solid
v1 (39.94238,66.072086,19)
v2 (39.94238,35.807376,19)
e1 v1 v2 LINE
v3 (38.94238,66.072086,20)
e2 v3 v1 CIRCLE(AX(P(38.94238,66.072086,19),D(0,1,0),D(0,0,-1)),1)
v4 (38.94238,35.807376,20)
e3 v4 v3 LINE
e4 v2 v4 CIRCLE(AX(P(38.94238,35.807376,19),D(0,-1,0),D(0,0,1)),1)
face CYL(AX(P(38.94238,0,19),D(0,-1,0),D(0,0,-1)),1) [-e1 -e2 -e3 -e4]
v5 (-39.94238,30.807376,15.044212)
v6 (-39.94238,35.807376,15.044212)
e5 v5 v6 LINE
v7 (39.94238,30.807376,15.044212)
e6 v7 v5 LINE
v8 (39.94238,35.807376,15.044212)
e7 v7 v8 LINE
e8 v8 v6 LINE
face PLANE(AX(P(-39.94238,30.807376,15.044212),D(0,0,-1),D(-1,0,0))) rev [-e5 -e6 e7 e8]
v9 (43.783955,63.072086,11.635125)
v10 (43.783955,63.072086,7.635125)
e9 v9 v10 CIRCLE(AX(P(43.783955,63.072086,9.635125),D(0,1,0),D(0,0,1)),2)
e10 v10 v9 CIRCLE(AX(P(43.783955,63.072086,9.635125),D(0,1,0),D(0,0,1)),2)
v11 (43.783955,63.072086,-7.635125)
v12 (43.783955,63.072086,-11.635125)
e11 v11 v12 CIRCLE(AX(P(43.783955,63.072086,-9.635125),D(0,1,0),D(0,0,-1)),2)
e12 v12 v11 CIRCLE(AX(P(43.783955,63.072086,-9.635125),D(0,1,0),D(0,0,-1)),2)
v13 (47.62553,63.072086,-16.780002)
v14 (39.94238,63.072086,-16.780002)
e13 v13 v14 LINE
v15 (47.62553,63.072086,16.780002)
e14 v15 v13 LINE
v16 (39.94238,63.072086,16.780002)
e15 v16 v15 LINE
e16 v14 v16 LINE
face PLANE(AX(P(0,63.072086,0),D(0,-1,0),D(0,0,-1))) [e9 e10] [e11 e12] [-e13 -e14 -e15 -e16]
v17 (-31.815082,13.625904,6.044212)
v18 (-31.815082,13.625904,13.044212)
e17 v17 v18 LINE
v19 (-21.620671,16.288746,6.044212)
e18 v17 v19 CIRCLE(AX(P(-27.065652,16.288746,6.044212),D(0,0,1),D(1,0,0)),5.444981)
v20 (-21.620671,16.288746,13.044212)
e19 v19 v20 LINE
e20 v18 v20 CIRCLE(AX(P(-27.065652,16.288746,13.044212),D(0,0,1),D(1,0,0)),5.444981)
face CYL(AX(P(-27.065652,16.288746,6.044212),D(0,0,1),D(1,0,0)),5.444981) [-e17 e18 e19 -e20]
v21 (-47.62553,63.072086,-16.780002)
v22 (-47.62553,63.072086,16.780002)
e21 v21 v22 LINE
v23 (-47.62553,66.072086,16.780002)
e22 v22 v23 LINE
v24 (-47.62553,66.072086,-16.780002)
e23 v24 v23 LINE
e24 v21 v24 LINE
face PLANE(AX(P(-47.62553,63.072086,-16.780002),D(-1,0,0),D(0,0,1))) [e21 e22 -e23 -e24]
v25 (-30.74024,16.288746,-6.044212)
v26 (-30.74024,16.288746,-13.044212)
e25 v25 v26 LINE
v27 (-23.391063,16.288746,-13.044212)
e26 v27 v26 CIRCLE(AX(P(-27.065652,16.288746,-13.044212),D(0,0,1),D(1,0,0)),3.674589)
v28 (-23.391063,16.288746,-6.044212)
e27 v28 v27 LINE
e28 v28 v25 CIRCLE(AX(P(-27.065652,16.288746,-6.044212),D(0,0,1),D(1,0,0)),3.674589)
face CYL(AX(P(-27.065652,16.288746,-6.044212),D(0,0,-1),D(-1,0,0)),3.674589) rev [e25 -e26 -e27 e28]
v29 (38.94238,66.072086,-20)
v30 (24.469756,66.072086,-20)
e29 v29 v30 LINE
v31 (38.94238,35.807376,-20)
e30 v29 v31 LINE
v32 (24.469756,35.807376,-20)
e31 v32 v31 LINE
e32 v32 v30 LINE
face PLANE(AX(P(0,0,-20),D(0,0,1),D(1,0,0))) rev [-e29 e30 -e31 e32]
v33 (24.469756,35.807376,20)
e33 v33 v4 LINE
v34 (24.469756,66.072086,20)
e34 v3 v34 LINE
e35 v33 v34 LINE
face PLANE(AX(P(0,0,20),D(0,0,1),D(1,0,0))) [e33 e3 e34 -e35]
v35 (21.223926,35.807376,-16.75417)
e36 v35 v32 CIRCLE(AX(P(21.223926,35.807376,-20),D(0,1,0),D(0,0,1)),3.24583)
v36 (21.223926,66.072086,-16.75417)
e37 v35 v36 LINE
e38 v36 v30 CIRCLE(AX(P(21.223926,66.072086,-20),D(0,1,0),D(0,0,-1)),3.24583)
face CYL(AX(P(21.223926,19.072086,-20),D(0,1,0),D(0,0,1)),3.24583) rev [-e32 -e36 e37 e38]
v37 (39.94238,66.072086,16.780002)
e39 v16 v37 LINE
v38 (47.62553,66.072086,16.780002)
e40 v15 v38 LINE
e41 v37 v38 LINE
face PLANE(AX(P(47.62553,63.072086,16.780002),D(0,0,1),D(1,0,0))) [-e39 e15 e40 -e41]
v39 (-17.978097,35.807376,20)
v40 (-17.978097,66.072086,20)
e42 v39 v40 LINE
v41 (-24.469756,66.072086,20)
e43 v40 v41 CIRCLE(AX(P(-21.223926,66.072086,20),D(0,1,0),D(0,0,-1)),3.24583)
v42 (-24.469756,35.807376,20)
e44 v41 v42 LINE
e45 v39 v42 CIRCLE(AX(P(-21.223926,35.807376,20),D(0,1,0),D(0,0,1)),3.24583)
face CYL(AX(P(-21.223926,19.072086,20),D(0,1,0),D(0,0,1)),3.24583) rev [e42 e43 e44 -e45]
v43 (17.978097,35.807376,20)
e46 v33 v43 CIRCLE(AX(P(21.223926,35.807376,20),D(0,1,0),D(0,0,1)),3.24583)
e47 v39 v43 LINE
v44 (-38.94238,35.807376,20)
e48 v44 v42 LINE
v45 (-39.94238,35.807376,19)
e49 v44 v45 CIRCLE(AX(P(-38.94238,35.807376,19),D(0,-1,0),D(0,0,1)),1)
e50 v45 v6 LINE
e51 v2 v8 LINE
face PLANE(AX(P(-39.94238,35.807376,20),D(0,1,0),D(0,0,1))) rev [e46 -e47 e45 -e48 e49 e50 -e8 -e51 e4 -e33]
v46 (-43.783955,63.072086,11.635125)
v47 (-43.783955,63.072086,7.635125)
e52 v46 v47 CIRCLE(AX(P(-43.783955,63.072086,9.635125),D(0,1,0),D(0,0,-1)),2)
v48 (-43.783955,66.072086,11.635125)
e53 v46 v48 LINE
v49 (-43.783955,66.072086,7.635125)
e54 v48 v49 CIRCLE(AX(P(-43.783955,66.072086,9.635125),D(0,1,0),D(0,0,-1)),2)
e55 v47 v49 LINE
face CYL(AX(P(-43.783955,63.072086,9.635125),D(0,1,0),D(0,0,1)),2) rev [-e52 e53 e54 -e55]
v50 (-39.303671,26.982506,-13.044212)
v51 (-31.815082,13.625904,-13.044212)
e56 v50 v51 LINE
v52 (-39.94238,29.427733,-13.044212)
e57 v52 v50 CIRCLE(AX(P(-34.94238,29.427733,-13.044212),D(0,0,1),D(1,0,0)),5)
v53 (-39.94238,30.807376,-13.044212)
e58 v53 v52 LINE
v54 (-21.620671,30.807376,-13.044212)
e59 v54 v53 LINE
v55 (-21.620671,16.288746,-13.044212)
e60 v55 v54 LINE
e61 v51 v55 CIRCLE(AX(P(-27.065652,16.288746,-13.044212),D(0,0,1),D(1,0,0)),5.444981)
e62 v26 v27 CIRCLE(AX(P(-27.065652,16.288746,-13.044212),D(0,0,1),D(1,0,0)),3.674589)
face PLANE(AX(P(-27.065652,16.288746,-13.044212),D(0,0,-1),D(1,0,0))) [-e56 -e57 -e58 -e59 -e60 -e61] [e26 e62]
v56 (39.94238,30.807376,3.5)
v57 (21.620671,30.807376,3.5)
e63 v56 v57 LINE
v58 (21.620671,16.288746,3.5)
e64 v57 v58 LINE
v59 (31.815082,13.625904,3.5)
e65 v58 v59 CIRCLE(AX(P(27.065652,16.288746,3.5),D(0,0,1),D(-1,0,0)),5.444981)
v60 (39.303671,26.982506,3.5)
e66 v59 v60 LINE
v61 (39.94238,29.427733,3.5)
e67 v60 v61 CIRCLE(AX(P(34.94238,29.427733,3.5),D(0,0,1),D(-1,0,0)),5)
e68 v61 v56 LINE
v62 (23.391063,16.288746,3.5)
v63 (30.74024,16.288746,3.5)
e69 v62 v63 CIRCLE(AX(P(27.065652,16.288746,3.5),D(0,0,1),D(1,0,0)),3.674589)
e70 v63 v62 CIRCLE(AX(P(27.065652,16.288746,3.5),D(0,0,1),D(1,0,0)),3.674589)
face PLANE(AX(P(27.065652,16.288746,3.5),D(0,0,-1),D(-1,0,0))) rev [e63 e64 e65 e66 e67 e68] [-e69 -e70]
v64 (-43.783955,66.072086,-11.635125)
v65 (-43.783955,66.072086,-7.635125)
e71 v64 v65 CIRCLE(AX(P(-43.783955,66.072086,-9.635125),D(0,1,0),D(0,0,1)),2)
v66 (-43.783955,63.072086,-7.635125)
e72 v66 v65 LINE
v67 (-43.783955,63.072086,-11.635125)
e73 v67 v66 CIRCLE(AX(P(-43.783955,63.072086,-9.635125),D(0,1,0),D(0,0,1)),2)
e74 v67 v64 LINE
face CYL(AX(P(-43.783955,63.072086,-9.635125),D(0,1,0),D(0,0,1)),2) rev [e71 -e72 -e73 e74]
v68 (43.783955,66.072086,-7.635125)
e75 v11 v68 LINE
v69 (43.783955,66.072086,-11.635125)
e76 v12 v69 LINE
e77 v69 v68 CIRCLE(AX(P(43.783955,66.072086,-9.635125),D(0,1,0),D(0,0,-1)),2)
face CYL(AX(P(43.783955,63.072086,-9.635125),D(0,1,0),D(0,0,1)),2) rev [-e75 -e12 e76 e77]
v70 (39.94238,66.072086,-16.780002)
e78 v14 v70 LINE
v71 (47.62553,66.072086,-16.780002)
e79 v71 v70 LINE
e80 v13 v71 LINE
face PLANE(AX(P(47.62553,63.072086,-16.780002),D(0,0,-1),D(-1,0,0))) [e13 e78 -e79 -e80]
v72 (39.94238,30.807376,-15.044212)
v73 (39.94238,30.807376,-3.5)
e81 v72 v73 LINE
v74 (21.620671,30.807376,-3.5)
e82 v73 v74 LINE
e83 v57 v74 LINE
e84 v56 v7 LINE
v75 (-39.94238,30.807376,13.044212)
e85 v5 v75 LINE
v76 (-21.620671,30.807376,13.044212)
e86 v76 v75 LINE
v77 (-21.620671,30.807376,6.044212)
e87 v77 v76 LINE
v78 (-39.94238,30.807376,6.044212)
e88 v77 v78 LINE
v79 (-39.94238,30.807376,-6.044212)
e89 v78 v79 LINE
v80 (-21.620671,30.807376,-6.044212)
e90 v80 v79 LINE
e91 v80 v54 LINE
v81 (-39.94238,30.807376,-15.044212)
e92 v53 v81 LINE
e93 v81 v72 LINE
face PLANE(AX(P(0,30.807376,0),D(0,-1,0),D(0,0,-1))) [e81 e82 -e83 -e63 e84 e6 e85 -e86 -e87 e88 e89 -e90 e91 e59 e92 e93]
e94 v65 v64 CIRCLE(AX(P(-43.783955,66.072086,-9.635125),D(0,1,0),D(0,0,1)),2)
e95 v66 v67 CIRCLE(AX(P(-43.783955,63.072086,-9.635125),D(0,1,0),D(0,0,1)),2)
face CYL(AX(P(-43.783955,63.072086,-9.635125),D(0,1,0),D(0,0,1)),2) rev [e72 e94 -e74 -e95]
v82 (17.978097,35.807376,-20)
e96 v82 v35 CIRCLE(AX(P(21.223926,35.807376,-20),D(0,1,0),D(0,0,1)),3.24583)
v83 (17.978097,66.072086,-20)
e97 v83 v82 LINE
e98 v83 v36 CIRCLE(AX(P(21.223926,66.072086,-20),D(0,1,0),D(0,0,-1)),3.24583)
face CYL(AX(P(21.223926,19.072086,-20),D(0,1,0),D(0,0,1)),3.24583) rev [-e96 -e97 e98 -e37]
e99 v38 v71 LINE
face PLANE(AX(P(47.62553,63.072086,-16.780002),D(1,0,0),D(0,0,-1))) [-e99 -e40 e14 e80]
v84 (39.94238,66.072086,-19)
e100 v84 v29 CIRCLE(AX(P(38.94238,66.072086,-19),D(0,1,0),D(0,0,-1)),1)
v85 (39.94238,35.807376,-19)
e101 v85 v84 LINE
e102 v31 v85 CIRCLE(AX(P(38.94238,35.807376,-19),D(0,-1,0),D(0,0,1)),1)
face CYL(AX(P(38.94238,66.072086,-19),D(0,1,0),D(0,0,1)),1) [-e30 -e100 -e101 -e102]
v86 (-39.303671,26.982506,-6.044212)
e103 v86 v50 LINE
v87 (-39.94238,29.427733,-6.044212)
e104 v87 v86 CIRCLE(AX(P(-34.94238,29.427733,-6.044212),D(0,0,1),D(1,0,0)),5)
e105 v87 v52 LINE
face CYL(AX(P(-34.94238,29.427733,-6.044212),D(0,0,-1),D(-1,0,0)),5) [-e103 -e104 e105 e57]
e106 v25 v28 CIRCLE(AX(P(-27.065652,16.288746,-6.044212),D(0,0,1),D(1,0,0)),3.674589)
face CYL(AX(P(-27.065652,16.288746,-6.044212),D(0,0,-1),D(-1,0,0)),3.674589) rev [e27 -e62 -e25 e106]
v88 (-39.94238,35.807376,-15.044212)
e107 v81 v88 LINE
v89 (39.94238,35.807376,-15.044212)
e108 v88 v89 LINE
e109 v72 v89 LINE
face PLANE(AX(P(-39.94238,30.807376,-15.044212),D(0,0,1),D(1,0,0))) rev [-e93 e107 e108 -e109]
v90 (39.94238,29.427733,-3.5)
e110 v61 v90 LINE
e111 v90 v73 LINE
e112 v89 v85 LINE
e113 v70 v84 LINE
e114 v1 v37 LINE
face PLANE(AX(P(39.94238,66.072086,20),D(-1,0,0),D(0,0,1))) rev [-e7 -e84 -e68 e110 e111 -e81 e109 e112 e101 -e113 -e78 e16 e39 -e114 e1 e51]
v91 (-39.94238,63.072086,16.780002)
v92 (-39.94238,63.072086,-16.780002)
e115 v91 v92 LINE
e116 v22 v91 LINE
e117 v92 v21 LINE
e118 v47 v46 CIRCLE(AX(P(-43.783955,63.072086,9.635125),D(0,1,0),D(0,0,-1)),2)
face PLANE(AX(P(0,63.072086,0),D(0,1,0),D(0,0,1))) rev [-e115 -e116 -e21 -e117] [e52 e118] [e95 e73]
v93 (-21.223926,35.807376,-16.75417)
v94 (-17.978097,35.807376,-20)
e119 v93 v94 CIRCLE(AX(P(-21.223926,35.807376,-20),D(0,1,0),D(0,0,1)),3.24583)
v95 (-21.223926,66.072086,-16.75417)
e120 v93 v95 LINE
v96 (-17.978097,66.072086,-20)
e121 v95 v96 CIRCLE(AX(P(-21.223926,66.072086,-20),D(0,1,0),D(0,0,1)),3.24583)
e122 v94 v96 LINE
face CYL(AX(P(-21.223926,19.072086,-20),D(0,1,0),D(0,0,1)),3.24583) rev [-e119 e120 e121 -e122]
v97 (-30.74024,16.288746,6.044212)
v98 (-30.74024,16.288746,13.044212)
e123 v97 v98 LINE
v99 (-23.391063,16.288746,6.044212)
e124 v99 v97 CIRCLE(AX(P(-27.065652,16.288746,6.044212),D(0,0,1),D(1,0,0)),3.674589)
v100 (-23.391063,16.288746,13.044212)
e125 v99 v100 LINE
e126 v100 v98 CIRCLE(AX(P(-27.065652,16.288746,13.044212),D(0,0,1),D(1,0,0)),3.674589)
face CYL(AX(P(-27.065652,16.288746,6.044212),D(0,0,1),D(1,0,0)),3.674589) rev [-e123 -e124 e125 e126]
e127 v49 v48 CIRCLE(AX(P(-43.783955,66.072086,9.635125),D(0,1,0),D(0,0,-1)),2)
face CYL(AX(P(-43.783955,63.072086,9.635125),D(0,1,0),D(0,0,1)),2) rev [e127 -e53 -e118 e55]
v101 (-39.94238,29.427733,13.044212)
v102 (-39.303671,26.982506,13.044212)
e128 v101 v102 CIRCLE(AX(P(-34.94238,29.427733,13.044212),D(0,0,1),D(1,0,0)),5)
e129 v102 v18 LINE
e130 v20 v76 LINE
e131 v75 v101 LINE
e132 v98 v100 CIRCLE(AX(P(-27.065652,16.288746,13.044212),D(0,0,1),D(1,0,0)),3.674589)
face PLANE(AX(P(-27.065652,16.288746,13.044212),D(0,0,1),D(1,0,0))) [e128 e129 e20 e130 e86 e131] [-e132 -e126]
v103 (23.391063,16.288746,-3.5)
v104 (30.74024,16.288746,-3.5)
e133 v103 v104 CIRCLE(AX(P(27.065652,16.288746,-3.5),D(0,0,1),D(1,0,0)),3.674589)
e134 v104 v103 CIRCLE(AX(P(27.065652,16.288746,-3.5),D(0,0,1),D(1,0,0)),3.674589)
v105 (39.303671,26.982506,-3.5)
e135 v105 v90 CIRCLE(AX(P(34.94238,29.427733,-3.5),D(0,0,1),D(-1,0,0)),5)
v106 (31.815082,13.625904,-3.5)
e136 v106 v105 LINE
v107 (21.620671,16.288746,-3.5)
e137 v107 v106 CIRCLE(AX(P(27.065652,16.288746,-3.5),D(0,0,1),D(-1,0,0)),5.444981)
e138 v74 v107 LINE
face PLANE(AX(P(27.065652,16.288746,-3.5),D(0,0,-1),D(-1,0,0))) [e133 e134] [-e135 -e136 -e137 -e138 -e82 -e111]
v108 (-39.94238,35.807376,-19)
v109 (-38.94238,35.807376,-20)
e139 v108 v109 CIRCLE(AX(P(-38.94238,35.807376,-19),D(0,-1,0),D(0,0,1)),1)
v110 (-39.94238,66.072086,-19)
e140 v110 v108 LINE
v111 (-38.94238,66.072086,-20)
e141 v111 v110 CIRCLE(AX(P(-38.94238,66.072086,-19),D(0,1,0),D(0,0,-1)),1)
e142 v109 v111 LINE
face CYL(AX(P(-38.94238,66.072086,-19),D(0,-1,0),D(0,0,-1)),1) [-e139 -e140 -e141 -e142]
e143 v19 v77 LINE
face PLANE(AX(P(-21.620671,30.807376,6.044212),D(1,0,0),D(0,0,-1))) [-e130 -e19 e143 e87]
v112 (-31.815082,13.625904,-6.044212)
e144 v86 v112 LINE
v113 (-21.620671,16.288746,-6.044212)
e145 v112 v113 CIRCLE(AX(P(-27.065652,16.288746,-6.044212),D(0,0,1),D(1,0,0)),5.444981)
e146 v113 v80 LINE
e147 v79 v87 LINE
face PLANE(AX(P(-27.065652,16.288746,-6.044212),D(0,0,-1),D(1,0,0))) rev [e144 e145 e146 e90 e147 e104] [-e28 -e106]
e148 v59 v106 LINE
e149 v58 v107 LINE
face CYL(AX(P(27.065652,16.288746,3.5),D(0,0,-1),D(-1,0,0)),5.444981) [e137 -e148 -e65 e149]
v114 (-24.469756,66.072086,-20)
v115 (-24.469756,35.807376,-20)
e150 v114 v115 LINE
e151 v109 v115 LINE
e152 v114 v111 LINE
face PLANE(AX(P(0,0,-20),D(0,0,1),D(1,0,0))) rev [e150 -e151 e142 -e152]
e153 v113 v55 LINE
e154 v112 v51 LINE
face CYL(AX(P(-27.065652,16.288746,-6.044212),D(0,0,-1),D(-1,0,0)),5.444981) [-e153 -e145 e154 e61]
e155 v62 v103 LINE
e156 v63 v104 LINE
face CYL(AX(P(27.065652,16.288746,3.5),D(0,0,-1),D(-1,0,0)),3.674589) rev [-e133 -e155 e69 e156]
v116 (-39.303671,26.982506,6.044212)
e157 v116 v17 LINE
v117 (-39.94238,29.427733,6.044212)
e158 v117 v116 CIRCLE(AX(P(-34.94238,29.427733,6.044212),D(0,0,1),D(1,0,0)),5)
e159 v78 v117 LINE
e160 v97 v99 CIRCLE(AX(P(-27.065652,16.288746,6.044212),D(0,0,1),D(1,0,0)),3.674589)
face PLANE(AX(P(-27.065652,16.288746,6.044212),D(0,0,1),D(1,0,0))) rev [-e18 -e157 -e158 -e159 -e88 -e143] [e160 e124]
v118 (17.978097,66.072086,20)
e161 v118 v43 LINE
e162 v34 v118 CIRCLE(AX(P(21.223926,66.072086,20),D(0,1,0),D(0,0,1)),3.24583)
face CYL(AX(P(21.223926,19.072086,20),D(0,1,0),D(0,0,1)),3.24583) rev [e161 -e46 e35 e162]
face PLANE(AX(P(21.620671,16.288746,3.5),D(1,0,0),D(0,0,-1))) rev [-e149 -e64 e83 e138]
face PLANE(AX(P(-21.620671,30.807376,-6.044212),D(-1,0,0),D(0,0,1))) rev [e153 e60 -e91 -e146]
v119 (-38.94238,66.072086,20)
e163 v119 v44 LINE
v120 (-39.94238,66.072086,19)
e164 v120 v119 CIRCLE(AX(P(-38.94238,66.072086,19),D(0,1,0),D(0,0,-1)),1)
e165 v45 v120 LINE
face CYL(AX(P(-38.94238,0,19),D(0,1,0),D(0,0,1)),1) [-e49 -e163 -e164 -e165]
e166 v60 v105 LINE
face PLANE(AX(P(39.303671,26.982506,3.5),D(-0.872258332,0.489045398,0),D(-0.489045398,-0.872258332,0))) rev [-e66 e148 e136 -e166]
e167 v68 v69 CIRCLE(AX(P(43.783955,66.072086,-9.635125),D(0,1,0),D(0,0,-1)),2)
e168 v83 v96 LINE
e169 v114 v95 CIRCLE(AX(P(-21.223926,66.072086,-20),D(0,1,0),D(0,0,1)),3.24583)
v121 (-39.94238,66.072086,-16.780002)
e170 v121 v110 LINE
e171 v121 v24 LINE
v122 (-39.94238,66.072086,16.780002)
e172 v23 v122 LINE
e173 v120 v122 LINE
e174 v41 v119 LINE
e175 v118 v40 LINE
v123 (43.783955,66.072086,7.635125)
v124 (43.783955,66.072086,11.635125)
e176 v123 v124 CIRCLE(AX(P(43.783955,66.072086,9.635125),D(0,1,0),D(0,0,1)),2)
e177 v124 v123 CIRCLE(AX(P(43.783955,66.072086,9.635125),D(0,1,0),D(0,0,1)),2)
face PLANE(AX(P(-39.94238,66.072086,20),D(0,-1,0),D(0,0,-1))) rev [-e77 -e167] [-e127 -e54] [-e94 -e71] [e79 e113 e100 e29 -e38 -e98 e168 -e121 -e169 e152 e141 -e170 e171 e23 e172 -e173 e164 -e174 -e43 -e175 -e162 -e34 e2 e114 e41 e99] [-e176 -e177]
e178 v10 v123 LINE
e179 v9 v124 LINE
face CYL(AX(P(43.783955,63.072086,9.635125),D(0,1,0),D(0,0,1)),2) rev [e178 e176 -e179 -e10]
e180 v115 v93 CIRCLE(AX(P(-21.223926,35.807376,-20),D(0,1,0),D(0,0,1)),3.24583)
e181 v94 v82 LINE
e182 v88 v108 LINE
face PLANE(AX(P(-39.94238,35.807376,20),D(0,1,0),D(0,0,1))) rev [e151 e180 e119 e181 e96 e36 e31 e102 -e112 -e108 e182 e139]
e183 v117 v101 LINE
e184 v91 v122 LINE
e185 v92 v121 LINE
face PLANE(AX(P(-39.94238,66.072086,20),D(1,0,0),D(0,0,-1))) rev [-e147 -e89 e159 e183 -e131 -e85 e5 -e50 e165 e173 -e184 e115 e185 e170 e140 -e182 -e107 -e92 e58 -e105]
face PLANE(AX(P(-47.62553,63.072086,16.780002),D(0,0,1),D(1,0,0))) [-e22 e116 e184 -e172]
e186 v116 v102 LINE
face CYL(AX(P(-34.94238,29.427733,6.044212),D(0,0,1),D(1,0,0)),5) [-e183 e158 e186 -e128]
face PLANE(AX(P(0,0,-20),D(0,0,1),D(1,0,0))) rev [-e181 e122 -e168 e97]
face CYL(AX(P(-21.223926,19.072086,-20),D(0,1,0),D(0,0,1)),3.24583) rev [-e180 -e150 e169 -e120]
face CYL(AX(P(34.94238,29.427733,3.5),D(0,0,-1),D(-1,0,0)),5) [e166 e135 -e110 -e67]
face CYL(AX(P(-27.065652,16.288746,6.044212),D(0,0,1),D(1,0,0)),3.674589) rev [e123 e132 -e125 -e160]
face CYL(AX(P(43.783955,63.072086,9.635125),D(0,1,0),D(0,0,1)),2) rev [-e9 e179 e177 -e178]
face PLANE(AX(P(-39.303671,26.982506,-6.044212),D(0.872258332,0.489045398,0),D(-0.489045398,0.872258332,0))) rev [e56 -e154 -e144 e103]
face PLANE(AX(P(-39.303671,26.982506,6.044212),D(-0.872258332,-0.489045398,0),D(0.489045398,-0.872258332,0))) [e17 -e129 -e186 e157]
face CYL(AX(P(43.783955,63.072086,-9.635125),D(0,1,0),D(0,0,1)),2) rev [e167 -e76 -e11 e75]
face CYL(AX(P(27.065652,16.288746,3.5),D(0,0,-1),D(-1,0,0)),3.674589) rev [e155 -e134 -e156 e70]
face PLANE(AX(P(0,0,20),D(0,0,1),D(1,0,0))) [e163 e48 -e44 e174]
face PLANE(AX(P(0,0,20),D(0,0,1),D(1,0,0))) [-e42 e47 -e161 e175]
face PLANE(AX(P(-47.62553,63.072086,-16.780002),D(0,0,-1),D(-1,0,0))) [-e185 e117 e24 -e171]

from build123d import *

# Parameters (mm, degrees)
SKETCH1_W           = 79.884759576
SKETCH1_H           = 30.264710677
BOSS_EXTRUDE1_DEPTH = 20
SKETCH2_W           = 79.884759576
SKETCH2_H           = 30.088424062
BOSS_EXTRUDE2_DEPTH = 5
SKETCH3_R           = 3.245829629
CUT_EXTRUDE1_DEPTH  = 47
FILLET1_R           = 1
SKETCH4_R           = 3.674588618
BOSS_EXTRUDE3_DEPTH = 7
SKETCH5_R           = 3.674588618
BOSS_EXTRUDE4_DEPTH = 3.5
SKETCH6_W           = 7.683150555
SKETCH6_H           = 33.560004606
SKETCH6_R           = 2
BOSS_EXTRUDE5_DEPTH = 3


with BuildPart() as part:
    # Sketch1 → Boss-Extrude1 (new, symmetric)
    with BuildSketch(Plane.XY):
        with Locations((0, 50.939731052)):
            Rectangle(SKETCH1_W, SKETCH1_H)
    extrude(amount=BOSS_EXTRUDE1_DEPTH, both=True)

    # Sketch2 → Boss-Extrude2 (add)
    with BuildSketch(Plane.XZ.offset(-35.807375713)):
        Rectangle(SKETCH2_W, SKETCH2_H)
    extrude(amount=BOSS_EXTRUDE2_DEPTH)

    # Sketch3 → Cut-Extrude1 (cut)
    with BuildSketch(Plane(origin=(0, 66.07208639, 0), x_dir=(1, 0, 0), z_dir=(0, 1, 0))):
        with Locations((-21.223926361, 20)):
            Circle(SKETCH3_R)
        with Locations((21.223926361, 20)):
            Circle(SKETCH3_R)
        with Locations((21.223926361, -20)):
            Circle(SKETCH3_R)
        with Locations((-21.223926361, -20)):
            Circle(SKETCH3_R)
    extrude(amount=-CUT_EXTRUDE1_DEPTH, mode=Mode.SUBTRACT)

    # Fillet1
    fillet1_edges = [part.edges().sort_by_distance(p)[0] for p in [
        (-39.942379788, 50.939731051, 20),
        (39.942379788, 50.939731051, 20),
        (-39.942379788, 50.939731051, -20),
        (39.942379788, 50.939731051, -20),
    ]]
    fillet(fillet1_edges, radius=FILLET1_R)

    # Sketch4 → Boss-Extrude3 (add)
    with BuildSketch(Plane.XY.offset(13.044212031)):
        with BuildLine():
            Line((-39.942379788, 30.807375713), (-39.942379788, 29.427732571))
            ThreePointArc((-39.942379788, 29.427732571), (-39.780068199, 28.164098588), (-39.303671451, 26.98250558))
            Line((-39.303671451, 26.98250558), (-31.815081757, 13.625903547))
            ThreePointArc((-31.815081757, 13.625903547), (-25.689559132, 11.020522164), (-21.620670757, 16.288746435))
            Line((-21.620670757, 16.288746435), (-21.620670757, 30.807375713))
            Line((-21.620670757, 30.807375713), (-39.942379788, 30.807375713))
        make_face()
        with Locations((-27.065651732, 16.288746435)):
            Circle(SKETCH4_R, mode=Mode.SUBTRACT)
    boss_extrude3 = extrude(amount=-BOSS_EXTRUDE3_DEPTH)

    # Mirror1: Boss-Extrude3 across plane
    add(boss_extrude3.mirror(Plane.XY))

    # Sketch5 → Boss-Extrude4 (add, symmetric)
    with BuildSketch(Plane.XY):
        with BuildLine():
            Line((21.620670757, 16.288746435), (21.620670757, 30.807375713))
            Line((21.620670757, 30.807375713), (39.942379788, 30.807375713))
            Line((39.942379788, 30.807375713), (39.942379788, 29.427732571))
            ThreePointArc((39.942379788, 29.427732571), (39.780068199, 28.164098588), (39.303671451, 26.98250558))
            Line((39.303671451, 26.98250558), (31.815081757, 13.625903547))
            ThreePointArc((31.815081757, 13.625903547), (25.689559132, 11.020522164), (21.620670757, 16.288746435))
        make_face()
        with Locations((27.065651732, 16.288746435)):
            Circle(SKETCH5_R, mode=Mode.SUBTRACT)
    extrude(amount=BOSS_EXTRUDE4_DEPTH, both=True)

    # Sketch6 → Boss-Extrude5 (add)
    # profile 1 of 2: a face of its own
    with BuildSketch(Plane(origin=(0, 66.07208639, 0), x_dir=(1, 0, 0), z_dir=(0, 1, 0))):
        with Locations((-43.783955066, 0)):
            Rectangle(SKETCH6_W, SKETCH6_H)
        with Locations(Location((-43.783955066, 9.635125017, 0), (0, 0, 270))):
            Circle(SKETCH6_R, mode=Mode.SUBTRACT)
        with Locations(Location((-43.783955066, -9.635125017, 0), (0, 0, 90))):
            Circle(SKETCH6_R, mode=Mode.SUBTRACT)
    # profile 2 of 2: a face of its own
    with BuildSketch(Plane(origin=(0, 66.07208639, 0), x_dir=(1, 0, 0), z_dir=(0, 1, 0))):
        with Locations((43.783955066, 0)):
            Rectangle(SKETCH6_W, SKETCH6_H)
        with Locations(Location((43.783955066, -9.635125017, 0), (0, 0, 270))):
            Circle(SKETCH6_R, mode=Mode.SUBTRACT)
        with Locations(Location((43.783955066, 9.635125017, 0), (0, 0, 90))):
            Circle(SKETCH6_R, mode=Mode.SUBTRACT)
    extrude(amount=-BOSS_EXTRUDE5_DEPTH)


solid = part.part
